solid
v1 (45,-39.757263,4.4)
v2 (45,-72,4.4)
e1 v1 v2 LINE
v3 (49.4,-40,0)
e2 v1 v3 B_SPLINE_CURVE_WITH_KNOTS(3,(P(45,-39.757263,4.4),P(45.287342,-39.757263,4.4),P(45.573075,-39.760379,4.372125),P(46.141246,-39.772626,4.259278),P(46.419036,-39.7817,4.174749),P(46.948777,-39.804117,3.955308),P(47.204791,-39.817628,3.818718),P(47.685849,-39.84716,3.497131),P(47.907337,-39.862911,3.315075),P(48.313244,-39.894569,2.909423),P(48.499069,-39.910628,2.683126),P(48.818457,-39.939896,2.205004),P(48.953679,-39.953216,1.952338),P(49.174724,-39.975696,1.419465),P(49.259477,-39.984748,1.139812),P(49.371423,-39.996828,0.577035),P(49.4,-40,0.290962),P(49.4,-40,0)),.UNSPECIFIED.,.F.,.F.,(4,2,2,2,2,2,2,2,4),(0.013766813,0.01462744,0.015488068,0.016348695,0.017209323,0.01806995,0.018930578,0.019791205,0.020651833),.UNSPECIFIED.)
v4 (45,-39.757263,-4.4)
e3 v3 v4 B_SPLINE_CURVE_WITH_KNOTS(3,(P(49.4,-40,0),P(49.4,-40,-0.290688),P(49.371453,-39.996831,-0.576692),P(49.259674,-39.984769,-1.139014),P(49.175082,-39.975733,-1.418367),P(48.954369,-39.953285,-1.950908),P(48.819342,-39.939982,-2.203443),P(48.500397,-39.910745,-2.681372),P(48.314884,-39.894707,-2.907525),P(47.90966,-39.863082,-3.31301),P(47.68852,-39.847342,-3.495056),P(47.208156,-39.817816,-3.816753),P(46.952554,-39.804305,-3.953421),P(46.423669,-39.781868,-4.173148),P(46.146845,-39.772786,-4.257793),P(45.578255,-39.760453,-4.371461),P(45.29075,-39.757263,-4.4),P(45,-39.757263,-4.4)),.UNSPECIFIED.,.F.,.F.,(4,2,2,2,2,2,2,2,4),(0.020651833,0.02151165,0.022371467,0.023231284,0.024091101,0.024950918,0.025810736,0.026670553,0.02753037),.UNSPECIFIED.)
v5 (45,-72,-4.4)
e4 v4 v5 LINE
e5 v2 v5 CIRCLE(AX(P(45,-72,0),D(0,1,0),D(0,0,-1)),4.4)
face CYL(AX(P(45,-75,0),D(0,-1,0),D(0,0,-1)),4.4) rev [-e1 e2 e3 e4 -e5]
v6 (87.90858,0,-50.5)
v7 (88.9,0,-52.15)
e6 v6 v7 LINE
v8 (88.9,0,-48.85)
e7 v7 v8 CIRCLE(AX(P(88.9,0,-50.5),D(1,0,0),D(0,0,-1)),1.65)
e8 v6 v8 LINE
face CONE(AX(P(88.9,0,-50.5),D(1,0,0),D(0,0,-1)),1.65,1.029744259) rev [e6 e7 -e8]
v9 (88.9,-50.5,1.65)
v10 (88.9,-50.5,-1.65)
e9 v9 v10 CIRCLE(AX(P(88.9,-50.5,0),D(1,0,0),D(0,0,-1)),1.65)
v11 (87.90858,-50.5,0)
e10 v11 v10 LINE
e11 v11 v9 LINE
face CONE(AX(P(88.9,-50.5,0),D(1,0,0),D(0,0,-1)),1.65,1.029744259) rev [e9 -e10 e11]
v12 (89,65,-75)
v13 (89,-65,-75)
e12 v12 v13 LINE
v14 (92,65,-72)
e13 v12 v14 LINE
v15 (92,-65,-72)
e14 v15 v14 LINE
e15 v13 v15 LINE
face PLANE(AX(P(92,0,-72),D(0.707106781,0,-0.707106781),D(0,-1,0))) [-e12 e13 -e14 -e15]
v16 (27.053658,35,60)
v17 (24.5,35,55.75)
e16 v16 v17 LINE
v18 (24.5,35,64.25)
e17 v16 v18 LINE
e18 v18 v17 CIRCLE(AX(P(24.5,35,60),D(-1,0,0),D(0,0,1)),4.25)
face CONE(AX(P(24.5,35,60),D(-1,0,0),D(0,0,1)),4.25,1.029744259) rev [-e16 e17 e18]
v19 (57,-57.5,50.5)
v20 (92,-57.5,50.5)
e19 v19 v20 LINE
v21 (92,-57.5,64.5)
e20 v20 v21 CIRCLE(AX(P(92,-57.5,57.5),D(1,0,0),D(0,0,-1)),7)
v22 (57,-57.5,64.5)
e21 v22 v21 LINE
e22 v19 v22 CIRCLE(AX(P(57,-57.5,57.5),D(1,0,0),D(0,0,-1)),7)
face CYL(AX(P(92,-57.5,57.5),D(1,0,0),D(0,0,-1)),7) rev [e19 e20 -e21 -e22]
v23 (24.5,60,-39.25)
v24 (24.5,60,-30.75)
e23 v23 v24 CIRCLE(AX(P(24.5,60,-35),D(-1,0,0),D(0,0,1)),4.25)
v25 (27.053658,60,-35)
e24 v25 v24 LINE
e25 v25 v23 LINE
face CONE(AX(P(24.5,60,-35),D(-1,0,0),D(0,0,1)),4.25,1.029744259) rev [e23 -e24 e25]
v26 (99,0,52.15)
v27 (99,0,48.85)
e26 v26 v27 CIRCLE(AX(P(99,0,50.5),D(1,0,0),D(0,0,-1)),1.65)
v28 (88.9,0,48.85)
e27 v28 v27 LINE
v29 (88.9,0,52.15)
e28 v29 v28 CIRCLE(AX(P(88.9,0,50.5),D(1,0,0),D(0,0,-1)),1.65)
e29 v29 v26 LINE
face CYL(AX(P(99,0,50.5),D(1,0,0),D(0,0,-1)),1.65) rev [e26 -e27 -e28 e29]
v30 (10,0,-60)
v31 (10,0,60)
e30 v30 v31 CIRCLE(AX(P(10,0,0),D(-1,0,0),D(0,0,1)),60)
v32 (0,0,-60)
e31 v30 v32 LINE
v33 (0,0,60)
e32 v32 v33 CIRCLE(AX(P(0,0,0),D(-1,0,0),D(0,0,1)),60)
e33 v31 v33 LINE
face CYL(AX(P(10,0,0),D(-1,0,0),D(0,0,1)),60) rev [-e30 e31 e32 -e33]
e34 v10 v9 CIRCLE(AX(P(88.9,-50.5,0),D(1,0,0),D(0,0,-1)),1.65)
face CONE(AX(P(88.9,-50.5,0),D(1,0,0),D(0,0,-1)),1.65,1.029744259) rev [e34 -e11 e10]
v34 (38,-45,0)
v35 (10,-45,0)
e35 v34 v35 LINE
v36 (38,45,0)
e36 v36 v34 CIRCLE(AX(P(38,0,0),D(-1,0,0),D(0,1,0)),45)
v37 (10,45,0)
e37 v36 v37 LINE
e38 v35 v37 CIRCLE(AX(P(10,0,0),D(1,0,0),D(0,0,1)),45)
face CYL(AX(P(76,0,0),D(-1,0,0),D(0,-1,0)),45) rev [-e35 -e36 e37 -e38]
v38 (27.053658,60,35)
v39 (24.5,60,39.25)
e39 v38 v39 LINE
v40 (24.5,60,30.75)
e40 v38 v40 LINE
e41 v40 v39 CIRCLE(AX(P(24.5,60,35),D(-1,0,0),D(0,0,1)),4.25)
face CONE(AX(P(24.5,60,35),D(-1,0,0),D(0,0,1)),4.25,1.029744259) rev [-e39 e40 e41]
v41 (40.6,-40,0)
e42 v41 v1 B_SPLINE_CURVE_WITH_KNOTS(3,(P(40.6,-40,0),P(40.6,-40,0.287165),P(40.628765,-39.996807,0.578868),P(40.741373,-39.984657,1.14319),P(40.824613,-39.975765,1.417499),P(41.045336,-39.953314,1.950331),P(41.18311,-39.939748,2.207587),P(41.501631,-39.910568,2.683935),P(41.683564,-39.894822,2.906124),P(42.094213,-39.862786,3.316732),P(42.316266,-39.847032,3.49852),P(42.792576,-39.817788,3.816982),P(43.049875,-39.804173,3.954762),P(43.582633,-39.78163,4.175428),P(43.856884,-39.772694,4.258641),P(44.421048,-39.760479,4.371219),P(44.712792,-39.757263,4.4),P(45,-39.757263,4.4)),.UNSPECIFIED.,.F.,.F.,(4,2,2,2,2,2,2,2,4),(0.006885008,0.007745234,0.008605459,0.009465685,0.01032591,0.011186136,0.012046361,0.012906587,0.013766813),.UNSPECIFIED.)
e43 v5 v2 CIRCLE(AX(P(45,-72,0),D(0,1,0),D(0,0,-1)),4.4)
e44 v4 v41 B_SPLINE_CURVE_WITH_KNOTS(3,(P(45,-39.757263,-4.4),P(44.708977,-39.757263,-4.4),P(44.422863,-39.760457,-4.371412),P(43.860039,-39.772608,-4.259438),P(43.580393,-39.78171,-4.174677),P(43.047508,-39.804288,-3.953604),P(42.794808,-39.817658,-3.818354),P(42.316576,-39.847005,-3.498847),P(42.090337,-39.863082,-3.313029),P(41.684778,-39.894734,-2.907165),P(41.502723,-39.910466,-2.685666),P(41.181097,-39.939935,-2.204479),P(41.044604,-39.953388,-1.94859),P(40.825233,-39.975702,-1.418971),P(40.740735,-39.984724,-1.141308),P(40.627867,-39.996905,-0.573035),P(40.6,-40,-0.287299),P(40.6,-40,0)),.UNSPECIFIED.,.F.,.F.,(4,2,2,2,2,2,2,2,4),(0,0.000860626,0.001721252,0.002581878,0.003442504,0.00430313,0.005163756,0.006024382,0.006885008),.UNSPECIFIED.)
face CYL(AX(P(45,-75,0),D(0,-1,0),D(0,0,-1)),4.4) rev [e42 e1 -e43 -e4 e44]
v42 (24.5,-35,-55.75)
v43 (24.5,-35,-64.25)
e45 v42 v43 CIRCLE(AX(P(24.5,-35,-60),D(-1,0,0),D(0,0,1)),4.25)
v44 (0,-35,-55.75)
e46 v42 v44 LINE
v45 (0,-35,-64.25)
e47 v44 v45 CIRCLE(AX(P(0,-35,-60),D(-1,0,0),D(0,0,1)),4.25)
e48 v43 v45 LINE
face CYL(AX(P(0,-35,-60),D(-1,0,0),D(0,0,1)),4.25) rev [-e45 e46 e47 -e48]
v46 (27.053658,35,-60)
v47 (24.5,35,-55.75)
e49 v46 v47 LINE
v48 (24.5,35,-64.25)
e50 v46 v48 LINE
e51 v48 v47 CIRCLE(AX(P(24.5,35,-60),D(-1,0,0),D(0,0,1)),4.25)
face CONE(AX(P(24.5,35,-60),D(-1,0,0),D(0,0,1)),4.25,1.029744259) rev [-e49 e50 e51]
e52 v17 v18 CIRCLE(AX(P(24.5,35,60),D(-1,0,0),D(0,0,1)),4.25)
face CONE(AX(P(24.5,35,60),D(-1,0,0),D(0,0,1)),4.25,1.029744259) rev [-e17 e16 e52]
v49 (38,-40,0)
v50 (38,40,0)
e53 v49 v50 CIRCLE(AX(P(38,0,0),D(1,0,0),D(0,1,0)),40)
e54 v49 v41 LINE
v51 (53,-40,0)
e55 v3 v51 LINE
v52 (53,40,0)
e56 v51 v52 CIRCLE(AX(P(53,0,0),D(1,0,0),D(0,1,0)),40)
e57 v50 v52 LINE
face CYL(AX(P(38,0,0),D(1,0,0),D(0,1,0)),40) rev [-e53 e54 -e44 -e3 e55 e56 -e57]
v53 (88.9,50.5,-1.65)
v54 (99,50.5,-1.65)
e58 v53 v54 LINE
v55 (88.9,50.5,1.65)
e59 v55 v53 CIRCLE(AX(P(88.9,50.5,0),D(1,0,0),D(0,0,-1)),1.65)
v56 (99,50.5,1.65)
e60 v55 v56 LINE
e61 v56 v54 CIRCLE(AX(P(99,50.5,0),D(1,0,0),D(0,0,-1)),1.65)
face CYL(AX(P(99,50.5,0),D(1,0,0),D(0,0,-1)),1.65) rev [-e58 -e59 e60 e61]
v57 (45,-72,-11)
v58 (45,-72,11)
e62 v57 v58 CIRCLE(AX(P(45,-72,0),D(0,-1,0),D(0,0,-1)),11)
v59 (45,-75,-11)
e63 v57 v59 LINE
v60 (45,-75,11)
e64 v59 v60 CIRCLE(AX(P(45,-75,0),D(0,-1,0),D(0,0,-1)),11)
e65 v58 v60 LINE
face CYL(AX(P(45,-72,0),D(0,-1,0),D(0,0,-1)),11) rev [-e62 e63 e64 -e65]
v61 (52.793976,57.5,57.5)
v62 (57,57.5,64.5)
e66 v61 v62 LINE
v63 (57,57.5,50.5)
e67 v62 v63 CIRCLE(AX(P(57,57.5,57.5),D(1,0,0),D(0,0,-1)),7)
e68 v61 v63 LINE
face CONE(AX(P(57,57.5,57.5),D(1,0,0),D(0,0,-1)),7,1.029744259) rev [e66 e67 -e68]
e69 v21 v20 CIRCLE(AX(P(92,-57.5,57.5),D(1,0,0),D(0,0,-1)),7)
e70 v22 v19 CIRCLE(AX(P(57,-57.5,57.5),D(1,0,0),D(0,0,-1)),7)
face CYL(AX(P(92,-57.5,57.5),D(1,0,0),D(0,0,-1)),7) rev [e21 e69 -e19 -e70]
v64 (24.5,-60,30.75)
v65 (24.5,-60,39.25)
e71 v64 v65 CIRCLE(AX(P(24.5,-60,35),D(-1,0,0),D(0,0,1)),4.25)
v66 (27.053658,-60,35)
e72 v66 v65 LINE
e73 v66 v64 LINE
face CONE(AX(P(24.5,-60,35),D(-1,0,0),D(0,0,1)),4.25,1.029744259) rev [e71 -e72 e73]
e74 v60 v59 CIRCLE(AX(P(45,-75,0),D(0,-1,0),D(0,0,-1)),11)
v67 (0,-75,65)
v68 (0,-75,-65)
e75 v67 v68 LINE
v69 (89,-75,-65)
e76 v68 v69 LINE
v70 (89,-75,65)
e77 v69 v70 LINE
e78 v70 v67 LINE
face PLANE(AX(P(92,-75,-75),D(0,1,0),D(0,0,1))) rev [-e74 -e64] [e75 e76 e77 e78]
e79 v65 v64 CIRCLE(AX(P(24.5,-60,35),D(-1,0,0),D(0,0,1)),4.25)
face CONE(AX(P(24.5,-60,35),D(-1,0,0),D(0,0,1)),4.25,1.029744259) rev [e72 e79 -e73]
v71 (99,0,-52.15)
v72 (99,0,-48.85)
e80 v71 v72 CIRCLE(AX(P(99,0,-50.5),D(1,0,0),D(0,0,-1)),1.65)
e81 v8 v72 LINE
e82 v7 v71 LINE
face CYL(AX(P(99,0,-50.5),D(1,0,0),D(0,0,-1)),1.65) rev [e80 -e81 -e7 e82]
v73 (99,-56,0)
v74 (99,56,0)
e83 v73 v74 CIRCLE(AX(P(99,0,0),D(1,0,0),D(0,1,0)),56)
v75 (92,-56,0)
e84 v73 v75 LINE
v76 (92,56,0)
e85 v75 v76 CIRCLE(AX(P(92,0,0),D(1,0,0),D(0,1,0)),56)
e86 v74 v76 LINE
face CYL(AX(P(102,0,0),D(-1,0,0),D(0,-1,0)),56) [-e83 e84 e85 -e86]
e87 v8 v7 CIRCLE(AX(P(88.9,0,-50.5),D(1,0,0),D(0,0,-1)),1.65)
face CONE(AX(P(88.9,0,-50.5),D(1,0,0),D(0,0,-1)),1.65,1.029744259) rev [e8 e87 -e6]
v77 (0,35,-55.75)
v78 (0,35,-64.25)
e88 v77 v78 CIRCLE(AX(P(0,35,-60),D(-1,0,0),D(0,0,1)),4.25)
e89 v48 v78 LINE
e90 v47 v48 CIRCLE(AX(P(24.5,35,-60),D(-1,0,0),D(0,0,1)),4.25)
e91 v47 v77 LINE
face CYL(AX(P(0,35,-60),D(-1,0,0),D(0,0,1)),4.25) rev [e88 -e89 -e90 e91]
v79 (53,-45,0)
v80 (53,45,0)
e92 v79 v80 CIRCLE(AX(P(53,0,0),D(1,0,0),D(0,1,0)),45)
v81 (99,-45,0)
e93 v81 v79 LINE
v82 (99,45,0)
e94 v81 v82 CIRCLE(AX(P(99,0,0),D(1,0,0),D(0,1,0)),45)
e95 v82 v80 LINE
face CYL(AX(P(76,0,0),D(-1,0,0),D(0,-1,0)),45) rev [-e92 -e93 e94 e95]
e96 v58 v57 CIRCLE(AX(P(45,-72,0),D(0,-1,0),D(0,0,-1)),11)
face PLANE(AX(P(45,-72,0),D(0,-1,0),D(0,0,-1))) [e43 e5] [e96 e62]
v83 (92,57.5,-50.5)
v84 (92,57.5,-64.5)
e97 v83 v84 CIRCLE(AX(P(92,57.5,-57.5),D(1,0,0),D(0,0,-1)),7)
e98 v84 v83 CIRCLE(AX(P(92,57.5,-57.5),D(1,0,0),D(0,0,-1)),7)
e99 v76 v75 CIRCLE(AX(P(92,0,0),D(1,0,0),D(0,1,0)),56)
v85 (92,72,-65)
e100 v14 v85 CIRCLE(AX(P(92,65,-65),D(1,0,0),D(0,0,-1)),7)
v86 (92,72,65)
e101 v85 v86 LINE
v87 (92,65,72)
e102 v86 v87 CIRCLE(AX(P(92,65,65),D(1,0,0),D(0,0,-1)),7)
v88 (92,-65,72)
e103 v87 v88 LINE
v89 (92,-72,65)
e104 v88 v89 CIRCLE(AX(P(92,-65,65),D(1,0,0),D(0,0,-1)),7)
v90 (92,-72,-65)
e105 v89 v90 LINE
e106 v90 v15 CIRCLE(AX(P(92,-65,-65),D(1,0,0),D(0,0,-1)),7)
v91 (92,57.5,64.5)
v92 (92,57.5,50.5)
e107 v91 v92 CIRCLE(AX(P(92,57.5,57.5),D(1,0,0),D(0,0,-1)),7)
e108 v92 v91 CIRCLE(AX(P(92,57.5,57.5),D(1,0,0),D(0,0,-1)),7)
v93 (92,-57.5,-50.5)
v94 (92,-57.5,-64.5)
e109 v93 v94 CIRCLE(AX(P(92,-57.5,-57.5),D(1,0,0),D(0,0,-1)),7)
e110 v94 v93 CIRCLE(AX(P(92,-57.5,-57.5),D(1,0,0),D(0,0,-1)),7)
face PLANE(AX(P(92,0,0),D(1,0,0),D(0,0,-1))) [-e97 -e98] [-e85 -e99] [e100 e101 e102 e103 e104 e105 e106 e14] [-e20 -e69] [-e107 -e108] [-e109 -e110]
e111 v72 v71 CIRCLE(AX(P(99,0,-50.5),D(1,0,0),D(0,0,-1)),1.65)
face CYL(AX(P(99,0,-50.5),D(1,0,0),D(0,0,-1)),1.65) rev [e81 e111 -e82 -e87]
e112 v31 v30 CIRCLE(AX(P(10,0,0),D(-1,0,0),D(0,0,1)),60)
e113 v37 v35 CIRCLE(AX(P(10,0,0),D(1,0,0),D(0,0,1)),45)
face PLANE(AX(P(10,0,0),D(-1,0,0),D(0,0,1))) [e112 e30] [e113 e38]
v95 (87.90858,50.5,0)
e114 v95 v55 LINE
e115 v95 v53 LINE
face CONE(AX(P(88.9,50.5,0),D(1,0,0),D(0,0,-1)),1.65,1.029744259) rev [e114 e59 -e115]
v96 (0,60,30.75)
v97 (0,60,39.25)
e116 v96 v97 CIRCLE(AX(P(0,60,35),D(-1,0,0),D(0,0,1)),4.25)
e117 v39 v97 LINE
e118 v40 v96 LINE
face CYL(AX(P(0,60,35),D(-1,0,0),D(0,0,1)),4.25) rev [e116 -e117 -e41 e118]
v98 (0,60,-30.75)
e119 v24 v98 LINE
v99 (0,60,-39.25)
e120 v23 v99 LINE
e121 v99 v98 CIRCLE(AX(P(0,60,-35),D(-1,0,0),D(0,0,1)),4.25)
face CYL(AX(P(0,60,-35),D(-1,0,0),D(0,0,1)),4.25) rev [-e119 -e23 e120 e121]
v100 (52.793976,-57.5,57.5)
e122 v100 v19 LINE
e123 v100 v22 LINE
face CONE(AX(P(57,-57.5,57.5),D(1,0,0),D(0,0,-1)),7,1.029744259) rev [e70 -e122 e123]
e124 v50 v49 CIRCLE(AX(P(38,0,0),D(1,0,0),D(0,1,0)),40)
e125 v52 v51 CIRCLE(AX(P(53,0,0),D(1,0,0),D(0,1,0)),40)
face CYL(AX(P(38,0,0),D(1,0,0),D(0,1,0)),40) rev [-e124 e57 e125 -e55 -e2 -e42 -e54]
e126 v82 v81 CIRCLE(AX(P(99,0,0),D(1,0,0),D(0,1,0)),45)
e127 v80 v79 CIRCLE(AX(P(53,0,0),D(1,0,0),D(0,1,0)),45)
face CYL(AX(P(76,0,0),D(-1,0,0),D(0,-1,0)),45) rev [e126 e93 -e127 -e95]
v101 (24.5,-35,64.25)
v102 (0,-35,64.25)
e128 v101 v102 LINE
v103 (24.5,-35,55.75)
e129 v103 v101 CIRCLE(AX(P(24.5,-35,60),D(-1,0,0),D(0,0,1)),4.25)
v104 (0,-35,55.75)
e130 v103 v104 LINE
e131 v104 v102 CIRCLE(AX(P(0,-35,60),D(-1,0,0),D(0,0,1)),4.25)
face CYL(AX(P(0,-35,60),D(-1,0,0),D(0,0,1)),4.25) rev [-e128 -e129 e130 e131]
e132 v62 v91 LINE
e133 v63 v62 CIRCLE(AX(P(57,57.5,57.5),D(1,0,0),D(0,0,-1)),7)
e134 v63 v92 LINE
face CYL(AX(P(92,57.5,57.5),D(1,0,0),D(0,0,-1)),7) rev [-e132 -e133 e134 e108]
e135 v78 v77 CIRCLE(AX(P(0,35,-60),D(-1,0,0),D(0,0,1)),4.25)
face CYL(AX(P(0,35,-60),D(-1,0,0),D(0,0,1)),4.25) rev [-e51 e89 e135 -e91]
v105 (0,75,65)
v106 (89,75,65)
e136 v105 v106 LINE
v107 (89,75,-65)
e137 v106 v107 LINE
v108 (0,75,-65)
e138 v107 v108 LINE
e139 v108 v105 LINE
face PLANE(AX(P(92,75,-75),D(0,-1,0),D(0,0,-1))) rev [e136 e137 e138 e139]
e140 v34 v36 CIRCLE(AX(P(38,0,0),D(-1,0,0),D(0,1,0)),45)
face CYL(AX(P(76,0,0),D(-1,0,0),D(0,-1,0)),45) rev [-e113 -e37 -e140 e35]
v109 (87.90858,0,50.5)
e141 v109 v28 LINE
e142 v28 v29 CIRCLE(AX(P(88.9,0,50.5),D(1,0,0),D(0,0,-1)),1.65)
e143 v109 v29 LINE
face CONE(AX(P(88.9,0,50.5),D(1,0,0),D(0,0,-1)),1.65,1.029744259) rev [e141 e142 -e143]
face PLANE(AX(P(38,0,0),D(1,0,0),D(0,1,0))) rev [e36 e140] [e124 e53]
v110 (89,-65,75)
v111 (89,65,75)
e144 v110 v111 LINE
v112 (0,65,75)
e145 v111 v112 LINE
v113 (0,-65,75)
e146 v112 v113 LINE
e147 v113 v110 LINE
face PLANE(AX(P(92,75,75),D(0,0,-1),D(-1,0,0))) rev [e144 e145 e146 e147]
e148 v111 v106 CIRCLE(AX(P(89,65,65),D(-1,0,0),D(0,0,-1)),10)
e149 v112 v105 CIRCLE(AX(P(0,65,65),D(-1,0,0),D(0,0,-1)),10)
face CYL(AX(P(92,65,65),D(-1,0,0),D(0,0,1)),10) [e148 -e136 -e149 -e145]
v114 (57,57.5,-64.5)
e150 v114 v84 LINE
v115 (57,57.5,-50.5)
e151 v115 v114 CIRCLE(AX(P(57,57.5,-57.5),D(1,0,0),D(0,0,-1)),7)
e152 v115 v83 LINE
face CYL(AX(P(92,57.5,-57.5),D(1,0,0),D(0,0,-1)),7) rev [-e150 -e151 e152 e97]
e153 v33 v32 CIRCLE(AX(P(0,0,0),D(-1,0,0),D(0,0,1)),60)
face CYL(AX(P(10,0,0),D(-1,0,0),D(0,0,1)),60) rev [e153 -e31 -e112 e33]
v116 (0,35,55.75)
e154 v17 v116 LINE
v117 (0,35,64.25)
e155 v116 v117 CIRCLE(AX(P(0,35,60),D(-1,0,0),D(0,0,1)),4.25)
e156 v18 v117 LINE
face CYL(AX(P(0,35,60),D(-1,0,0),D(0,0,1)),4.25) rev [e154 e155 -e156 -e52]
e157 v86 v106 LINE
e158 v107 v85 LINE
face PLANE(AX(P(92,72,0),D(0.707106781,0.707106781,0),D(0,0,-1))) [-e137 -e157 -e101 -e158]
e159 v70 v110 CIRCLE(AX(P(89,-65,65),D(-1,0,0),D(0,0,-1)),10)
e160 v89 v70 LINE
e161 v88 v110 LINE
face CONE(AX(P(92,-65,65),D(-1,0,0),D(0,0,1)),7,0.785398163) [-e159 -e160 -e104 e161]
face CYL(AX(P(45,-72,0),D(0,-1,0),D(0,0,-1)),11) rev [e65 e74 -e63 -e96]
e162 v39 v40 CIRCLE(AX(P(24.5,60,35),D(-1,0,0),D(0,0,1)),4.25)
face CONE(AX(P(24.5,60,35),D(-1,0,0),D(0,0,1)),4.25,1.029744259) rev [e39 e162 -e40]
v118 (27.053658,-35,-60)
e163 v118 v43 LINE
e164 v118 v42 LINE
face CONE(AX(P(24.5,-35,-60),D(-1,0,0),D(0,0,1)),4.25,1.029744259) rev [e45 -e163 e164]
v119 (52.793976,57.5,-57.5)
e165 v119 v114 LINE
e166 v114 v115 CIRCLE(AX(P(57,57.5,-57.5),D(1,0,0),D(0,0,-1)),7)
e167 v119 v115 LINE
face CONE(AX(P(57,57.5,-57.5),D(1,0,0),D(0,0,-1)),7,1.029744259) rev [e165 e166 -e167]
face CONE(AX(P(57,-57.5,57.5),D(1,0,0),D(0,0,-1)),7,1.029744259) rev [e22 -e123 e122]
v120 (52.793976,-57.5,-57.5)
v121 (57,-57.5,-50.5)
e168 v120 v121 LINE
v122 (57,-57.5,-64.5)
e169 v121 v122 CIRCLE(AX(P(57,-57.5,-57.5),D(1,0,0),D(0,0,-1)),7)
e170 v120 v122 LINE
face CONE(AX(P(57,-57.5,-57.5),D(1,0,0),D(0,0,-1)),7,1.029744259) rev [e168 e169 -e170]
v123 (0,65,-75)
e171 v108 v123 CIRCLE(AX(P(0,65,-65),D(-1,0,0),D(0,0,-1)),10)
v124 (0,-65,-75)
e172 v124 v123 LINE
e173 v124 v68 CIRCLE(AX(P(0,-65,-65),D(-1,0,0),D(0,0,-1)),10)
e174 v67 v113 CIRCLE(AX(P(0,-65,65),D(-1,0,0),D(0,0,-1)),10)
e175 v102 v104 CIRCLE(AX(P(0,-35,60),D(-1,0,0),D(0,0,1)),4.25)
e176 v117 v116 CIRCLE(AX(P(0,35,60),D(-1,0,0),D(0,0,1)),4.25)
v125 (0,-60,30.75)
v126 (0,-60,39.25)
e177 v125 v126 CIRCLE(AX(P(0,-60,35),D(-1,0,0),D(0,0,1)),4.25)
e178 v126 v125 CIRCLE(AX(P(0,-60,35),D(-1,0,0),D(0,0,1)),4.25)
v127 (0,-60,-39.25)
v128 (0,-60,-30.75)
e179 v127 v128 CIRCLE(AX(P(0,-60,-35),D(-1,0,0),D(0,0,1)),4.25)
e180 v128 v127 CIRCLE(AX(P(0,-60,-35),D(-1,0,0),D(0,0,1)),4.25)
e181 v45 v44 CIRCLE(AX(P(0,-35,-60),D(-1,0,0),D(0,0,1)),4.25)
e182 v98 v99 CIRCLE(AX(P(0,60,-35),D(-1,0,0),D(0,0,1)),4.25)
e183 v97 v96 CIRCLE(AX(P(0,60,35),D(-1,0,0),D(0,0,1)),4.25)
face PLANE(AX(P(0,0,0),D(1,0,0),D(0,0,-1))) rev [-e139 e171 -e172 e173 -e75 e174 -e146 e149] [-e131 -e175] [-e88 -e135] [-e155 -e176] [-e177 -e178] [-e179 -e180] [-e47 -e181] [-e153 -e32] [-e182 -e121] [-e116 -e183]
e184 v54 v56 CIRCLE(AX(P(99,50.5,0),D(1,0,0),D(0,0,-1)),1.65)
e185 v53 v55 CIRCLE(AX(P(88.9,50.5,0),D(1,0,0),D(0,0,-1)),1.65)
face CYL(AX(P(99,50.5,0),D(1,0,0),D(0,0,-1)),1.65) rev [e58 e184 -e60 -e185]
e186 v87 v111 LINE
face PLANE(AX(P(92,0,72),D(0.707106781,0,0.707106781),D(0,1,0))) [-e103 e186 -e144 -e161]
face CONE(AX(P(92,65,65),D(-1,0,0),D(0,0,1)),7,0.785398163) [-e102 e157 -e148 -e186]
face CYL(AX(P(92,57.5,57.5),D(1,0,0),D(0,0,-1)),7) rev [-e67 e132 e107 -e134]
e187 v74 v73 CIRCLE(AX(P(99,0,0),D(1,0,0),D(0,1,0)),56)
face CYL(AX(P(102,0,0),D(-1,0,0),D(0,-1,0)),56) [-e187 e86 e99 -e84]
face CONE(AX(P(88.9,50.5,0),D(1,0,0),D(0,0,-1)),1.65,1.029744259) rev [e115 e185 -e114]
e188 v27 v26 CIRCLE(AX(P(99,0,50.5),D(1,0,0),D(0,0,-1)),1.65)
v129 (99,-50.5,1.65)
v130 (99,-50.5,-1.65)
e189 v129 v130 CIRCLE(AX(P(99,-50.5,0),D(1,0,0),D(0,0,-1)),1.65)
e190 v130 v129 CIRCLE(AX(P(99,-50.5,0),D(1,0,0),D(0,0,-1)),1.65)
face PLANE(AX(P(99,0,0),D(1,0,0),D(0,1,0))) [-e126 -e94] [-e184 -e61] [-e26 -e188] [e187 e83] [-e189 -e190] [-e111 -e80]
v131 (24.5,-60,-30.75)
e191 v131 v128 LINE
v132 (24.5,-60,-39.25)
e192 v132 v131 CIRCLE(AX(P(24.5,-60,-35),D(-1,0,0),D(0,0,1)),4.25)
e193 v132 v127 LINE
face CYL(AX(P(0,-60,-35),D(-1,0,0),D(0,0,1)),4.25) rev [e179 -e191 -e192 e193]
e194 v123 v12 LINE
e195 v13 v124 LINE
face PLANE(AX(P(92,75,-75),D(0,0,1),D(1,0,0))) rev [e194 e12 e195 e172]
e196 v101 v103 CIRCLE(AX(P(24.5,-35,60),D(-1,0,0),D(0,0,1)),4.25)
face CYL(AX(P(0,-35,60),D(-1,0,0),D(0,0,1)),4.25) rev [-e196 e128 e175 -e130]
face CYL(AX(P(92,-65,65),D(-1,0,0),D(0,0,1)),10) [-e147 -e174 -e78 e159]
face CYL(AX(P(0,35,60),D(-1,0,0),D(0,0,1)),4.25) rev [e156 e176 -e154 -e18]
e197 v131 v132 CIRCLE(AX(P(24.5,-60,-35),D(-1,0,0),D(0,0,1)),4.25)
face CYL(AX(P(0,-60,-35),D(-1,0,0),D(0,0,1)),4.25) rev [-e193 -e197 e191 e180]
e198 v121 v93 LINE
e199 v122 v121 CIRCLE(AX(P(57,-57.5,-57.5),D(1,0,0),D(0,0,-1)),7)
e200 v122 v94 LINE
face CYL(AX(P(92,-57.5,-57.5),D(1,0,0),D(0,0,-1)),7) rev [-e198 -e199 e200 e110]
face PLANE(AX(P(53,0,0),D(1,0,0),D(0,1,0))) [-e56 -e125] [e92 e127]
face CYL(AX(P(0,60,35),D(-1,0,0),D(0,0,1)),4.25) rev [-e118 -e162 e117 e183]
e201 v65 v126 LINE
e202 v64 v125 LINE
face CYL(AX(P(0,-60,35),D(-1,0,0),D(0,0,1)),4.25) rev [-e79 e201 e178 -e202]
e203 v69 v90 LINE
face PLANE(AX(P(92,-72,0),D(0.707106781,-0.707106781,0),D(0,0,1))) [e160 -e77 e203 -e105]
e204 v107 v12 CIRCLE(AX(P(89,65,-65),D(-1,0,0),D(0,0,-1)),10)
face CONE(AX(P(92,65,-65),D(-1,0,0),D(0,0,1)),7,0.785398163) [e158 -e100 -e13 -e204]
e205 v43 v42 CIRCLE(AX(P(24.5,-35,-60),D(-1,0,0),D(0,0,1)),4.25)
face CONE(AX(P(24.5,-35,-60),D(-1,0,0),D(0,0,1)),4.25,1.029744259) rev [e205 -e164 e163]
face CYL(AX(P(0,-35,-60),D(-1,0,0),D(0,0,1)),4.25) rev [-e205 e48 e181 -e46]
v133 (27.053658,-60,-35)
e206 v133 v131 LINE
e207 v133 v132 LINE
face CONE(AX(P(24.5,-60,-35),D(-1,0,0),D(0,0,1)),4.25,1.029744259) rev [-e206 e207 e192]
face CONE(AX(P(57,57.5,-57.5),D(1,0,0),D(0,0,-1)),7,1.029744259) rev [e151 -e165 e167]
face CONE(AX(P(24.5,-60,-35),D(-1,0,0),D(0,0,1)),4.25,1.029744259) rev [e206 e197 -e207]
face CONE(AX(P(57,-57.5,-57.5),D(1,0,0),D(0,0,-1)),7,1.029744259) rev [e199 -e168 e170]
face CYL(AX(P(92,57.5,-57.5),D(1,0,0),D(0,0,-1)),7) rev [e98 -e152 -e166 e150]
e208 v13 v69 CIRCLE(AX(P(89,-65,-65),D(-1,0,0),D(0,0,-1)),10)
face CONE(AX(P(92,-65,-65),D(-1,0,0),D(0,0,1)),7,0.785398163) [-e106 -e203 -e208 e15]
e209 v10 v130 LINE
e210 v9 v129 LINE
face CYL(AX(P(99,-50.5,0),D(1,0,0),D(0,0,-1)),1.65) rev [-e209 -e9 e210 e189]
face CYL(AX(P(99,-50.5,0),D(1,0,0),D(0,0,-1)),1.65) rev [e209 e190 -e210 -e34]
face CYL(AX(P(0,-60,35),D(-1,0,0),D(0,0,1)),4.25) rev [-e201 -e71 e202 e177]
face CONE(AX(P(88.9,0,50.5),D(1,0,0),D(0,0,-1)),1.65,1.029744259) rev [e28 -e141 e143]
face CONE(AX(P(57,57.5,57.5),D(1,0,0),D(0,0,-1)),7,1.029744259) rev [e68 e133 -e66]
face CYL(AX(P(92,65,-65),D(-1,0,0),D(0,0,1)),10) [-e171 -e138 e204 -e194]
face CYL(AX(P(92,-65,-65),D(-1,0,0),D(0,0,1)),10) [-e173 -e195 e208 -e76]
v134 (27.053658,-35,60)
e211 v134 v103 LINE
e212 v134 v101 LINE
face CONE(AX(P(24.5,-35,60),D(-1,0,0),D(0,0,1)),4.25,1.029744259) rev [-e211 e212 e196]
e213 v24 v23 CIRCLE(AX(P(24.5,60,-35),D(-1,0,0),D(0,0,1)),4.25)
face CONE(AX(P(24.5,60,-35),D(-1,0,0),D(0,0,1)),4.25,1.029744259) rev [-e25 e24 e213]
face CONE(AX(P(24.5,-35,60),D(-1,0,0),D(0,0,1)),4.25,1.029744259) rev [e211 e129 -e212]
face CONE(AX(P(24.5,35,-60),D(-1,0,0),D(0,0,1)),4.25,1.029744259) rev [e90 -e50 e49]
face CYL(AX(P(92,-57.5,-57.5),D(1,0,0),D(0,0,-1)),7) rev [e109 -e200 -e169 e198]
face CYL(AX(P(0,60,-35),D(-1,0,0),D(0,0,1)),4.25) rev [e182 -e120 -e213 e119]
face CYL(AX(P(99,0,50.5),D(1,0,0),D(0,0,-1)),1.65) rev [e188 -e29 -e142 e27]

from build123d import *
from build123d.topology import SkipClean

# Parameters (mm, degrees)
SKETCH1_W               = 150
SKETCH1_H               = 150
BOSS_EXTRUDE1_DEPTH     = 92
SKETCH2_R               = 56
BOSS_EXTRUDE2_DEPTH     = 10
SKETCH3_R               = 45
CUT_EXTRUDE1_DEPTH      = 76
SKETCH4_R               = 38.5
CUT_EXTRUDE2_DEPTH      = 49
M10_TAPPED_HOLE1_D      = 8.5
M10_TAPPED_HOLE1_DEPTH  = 24.5
M10_TAPPED_HOLE1_TIP    = 2.553657631
M16_TAPPED_HOLE1_D      = 14
M16_TAPPED_HOLE1_DEPTH  = 35
M16_TAPPED_HOLE1_TIP    = 4.206024333
SKETCH14_R              = 55
CUT_EXTRUDE5_DEPTH      = 3
CHAMFER2_SIZE           = 0.5
SKETCH23_R              = 51.5
SKETCH23_R_2            = 41.5
CUT_EXTRUDE9_DEPTH      = 3
CIRPATTERN1_COUNT       = 4
FILLET1_R               = 10
CHAMFER6_SIZE           = 3
SKETCH30_R              = 2.5
CUT_EXTRUDE12_DEPTH     = 12
G1_8_TAPPED_HOLE1_D     = 8.8
G1_8_TAPPED_HOLE1_DEPTH = 30
G1_8_TAPPED_HOLE1_TIP   = 2.643786724
SKETCH34_R              = 11
CUT_EXTRUDE14_DEPTH     = 3
SKETCH35_R              = 60
CUT_EXTRUDE15_DEPTH     = 10
SKETCH36_R              = 55
SKETCH36_R_2            = 38.5
BOSS_EXTRUDE3_DEPTH     = 3
SKETCH37_R              = 95.296679702
CUT_EXTRUDE16_DEPTH     = 3
BOSS_EXTRUDE4_START     = -61
SKETCH38_R              = 45
SKETCH38_R_2            = 40
BOSS_EXTRUDE4_DEPTH     = 15
CUT_EXTRUDE17_START     = -23
SKETCH39_R              = 45
CUT_EXTRUDE17_DEPTH     = 23
CUT_EXTRUDE18_REACH     = 194.445
SKETCH40_R              = 4.4


with BuildPart() as part:
    # Sketch1 → Boss-Extrude1 (new body)
    with BuildSketch(Plane(origin=(0, 0, 0), x_dir=(0, -1, 0), z_dir=(1, 0, 0))):
        Rectangle(SKETCH1_W, SKETCH1_H)
    extrude(amount=BOSS_EXTRUDE1_DEPTH)

    # Sketch2 → Boss-Extrude2 (add)
    with BuildSketch(Plane(origin=(92, 0, 0), x_dir=(0, -1, 0), z_dir=(1, 0, 0))):
        with Locations(Location((0, 0, 0), (0, 0, 180))):
            Circle(SKETCH2_R)
    extrude(amount=BOSS_EXTRUDE2_DEPTH)

    # Sketch3 → Cut-Extrude1 (cut)
    with BuildSketch(Plane(origin=(0, 0, 0), x_dir=(0, -1, 0), z_dir=(-1, 0, 0))):
        Circle(SKETCH3_R)
    extrude(amount=-CUT_EXTRUDE1_DEPTH, mode=Mode.SUBTRACT)

    # Sketch4 → Cut-Extrude2 (cut)
    with BuildSketch(Plane(origin=(102, 0, 0), x_dir=(0, -1, 0), z_dir=(1, 0, 0))):
        with Locations(Location((0, 0, 0), (0, 0, 180))):
            Circle(SKETCH4_R)
    extrude(amount=-CUT_EXTRUDE2_DEPTH, mode=Mode.SUBTRACT)

    # M10 Tapped Hole1
    with Locations(Plane(origin=(0, 0, 0), x_dir=(0, 1, 0), z_dir=(-1, 0, 0))):
        with Locations((-35, 60), (35, 60), (60, 35), (60, -35), (35, -60), (-35, -60), (-60, -35), (-60, 35)):
            Hole(M10_TAPPED_HOLE1_D / 2, depth=M10_TAPPED_HOLE1_DEPTH)
            with Locations((0, 0, -(M10_TAPPED_HOLE1_DEPTH + M10_TAPPED_HOLE1_TIP / 2))):  # 118° drill point
                Cone(0, M10_TAPPED_HOLE1_D / 2, M10_TAPPED_HOLE1_TIP, mode=Mode.SUBTRACT)

    # M16 Tapped Hole1
    with Locations(Plane(origin=(92, 0, 0), x_dir=(0, -1, 0), z_dir=(1, 0, 0))):
        with Locations((57.5, 57.5), (-57.5, 57.5), (-57.5, -57.5), (57.5, -57.5)):
            Hole(M16_TAPPED_HOLE1_D / 2, depth=M16_TAPPED_HOLE1_DEPTH)
            with Locations((0, 0, -(M16_TAPPED_HOLE1_DEPTH + M16_TAPPED_HOLE1_TIP / 2))):  # 118° drill point
                Cone(0, M16_TAPPED_HOLE1_D / 2, M16_TAPPED_HOLE1_TIP, mode=Mode.SUBTRACT)

    # Sketch14 → Cut-Extrude5 (cut)
    with BuildSketch(Plane(origin=(76, 0, 0), x_dir=(0, -1, 0), z_dir=(-1, 0, 0))):
        Circle(SKETCH14_R)
    extrude(amount=-CUT_EXTRUDE5_DEPTH, mode=Mode.SUBTRACT)

    # Chamfer2
    chamfer2_edges = [part.edges().sort_by_distance(p)[0] for p in [
        (102, -56, 0),
    ]]
    chamfer(chamfer2_edges, length=CHAMFER2_SIZE)

    # Sketch23 → Cut-Extrude9 (cut)
    with BuildSketch(Plane(origin=(102, 0, 0), x_dir=(0, 0, -1), z_dir=(1, 0, 0))):
        with Locations(Location((0, 0, 0), (0, 0, 90))):
            Circle(SKETCH23_R)
        with Locations(Location((0, 0, 0), (0, 0, 90))):
            Circle(SKETCH23_R_2, mode=Mode.SUBTRACT)
    extrude(amount=-CUT_EXTRUDE9_DEPTH, mode=Mode.SUBTRACT)

    # Sketch25 → M4 Tapped Hole2 (revolve, cut)
    with BuildSketch(Plane(origin=(99, 50.5, 0), x_dir=(0, 0, -1), z_dir=(0, 1, 0))):
        Polygon((0, 0), (0, 11.091420021), (1.65, 10.1), (1.65, 0), align=None)
    m4_tapped_hole2 = revolve(axis=Axis((105.35, 50.5, 0), (-1, 0, 0)), mode=Mode.SUBTRACT)

    # CirPattern1: M4 Tapped Hole2 ×4 about axis
    cirpattern1_axis = Axis((0, 0, 0), (1, 0, 0))
    for i in range(1, CIRPATTERN1_COUNT):
        add(m4_tapped_hole2.rotate(cirpattern1_axis, i * 360 / CIRPATTERN1_COUNT), mode=Mode.SUBTRACT)

    # Fillet1
    fillet1_edges = [part.edges().sort_by_distance(p)[0] for p in [
        (46, -75, 75),
        (46, 75, 75),
        (46, 75, -75),
        (46, -75, -75),
    ]]
    fillet(fillet1_edges, radius=FILLET1_R)

    # Chamfer6
    chamfer6_edges = [part.edges().sort_by_distance(p)[0] for p in [
        (92, 0, -75),
        (92, -75, 0),
        (92, 75, 0),
        (92, 0, 75),
        (92, 72.071067812, 72.071067812),
        (92, 72.071067812, -72.071067812),
        (92, -72.071067812, 72.071067812),
        (92, -72.071067812, -72.071067812),
    ]]
    chamfer(chamfer6_edges, length=CHAMFER6_SIZE)

    # Sketch30 → Cut-Extrude12 (cut)
    with BuildSketch(Plane.XZ.offset(75)):
        with Locations(Location((45, 0, 0), (0, 0, 270))):
            Circle(SKETCH30_R)
    extrude(amount=-CUT_EXTRUDE12_DEPTH, mode=Mode.SUBTRACT)

    # G1/8 Tapped Hole1
    with Locations(Plane(origin=(0, -75, 0), x_dir=(-1, 0, 0), z_dir=(0, -1, 0))):
        with Locations((-45, 0)):
            Hole(G1_8_TAPPED_HOLE1_D / 2, depth=G1_8_TAPPED_HOLE1_DEPTH)
            with Locations((0, 0, -(G1_8_TAPPED_HOLE1_DEPTH + G1_8_TAPPED_HOLE1_TIP / 2))):  # 118° drill point
                Cone(0, G1_8_TAPPED_HOLE1_D / 2, G1_8_TAPPED_HOLE1_TIP, mode=Mode.SUBTRACT)

    # Sketch34 → Cut-Extrude14 (cut)
    with BuildSketch(Plane.XZ.offset(75)):
        with Locations(Location((45, 0, 0), (0, 0, 270))):
            Circle(SKETCH34_R)
    extrude(amount=-CUT_EXTRUDE14_DEPTH, mode=Mode.SUBTRACT)

    # Sketch35 → Cut-Extrude15 (cut)
    with BuildSketch(Plane.ZY):
        Circle(SKETCH35_R)
    extrude(amount=-CUT_EXTRUDE15_DEPTH, mode=Mode.SUBTRACT)

    # Sketch36 → Boss-Extrude3 (add)
    with BuildSketch(Plane.ZY.offset(-79)):
        Circle(SKETCH36_R)
        with Locations(Location((0, 0, 0), (0, 0, 90))):
            Circle(SKETCH36_R_2, mode=Mode.SUBTRACT)
    extrude(amount=BOSS_EXTRUDE3_DEPTH)

    # Sketch37 → Cut-Extrude16 (cut)
    with BuildSketch(Plane(origin=(102, 0, 0), x_dir=(0, 0, -1), z_dir=(1, 0, 0))):
        Circle(SKETCH37_R)
    extrude(amount=-CUT_EXTRUDE16_DEPTH, mode=Mode.SUBTRACT)

    # Sketch38 → Boss-Extrude4 (add)
    with BuildSketch(Plane(origin=(99, 0, 0), x_dir=(0, 0, -1), z_dir=(1, 0, 0)).offset(BOSS_EXTRUDE4_START)):
        with Locations(Location((0, 0, 0), (0, 0, 180))):
            Circle(SKETCH38_R)
        with Locations(Location((0, 0, 0), (0, 0, 90))):
            Circle(SKETCH38_R_2, mode=Mode.SUBTRACT)
    extrude(amount=BOSS_EXTRUDE4_DEPTH)

    # Sketch39 → Cut-Extrude17 (cut)
    with SkipClean():  # the faces are left unmerged after this step: merging them gives an invalid solid
        with BuildSketch(Plane(origin=(99, 0, 0), x_dir=(0, 0, -1), z_dir=(1, 0, 0)).offset(CUT_EXTRUDE17_START)):
            with Locations(Location((0, 0, 0), (0, 0, 180))):
                Circle(SKETCH39_R)
        extrude(amount=CUT_EXTRUDE17_DEPTH, mode=Mode.SUBTRACT)

    # Sketch40 → Cut-Extrude18 (cut, up to next)
    with BuildSketch(Plane.XZ.offset(72), mode=Mode.PRIVATE) as cut_extrude18_sk1:
        with Locations(Location((45, 0, 0), (0, 0, 270))):
            Circle(SKETCH40_R)
    cut_extrude18_tool1 = extrude(cut_extrude18_sk1.sketch, amount=-CUT_EXTRUDE18_REACH, mode=Mode.PRIVATE) & part.part
    add(cut_extrude18_tool1.solids().sort_by_distance((45, -72, 0))[0], mode=Mode.SUBTRACT)


solid = part.part
